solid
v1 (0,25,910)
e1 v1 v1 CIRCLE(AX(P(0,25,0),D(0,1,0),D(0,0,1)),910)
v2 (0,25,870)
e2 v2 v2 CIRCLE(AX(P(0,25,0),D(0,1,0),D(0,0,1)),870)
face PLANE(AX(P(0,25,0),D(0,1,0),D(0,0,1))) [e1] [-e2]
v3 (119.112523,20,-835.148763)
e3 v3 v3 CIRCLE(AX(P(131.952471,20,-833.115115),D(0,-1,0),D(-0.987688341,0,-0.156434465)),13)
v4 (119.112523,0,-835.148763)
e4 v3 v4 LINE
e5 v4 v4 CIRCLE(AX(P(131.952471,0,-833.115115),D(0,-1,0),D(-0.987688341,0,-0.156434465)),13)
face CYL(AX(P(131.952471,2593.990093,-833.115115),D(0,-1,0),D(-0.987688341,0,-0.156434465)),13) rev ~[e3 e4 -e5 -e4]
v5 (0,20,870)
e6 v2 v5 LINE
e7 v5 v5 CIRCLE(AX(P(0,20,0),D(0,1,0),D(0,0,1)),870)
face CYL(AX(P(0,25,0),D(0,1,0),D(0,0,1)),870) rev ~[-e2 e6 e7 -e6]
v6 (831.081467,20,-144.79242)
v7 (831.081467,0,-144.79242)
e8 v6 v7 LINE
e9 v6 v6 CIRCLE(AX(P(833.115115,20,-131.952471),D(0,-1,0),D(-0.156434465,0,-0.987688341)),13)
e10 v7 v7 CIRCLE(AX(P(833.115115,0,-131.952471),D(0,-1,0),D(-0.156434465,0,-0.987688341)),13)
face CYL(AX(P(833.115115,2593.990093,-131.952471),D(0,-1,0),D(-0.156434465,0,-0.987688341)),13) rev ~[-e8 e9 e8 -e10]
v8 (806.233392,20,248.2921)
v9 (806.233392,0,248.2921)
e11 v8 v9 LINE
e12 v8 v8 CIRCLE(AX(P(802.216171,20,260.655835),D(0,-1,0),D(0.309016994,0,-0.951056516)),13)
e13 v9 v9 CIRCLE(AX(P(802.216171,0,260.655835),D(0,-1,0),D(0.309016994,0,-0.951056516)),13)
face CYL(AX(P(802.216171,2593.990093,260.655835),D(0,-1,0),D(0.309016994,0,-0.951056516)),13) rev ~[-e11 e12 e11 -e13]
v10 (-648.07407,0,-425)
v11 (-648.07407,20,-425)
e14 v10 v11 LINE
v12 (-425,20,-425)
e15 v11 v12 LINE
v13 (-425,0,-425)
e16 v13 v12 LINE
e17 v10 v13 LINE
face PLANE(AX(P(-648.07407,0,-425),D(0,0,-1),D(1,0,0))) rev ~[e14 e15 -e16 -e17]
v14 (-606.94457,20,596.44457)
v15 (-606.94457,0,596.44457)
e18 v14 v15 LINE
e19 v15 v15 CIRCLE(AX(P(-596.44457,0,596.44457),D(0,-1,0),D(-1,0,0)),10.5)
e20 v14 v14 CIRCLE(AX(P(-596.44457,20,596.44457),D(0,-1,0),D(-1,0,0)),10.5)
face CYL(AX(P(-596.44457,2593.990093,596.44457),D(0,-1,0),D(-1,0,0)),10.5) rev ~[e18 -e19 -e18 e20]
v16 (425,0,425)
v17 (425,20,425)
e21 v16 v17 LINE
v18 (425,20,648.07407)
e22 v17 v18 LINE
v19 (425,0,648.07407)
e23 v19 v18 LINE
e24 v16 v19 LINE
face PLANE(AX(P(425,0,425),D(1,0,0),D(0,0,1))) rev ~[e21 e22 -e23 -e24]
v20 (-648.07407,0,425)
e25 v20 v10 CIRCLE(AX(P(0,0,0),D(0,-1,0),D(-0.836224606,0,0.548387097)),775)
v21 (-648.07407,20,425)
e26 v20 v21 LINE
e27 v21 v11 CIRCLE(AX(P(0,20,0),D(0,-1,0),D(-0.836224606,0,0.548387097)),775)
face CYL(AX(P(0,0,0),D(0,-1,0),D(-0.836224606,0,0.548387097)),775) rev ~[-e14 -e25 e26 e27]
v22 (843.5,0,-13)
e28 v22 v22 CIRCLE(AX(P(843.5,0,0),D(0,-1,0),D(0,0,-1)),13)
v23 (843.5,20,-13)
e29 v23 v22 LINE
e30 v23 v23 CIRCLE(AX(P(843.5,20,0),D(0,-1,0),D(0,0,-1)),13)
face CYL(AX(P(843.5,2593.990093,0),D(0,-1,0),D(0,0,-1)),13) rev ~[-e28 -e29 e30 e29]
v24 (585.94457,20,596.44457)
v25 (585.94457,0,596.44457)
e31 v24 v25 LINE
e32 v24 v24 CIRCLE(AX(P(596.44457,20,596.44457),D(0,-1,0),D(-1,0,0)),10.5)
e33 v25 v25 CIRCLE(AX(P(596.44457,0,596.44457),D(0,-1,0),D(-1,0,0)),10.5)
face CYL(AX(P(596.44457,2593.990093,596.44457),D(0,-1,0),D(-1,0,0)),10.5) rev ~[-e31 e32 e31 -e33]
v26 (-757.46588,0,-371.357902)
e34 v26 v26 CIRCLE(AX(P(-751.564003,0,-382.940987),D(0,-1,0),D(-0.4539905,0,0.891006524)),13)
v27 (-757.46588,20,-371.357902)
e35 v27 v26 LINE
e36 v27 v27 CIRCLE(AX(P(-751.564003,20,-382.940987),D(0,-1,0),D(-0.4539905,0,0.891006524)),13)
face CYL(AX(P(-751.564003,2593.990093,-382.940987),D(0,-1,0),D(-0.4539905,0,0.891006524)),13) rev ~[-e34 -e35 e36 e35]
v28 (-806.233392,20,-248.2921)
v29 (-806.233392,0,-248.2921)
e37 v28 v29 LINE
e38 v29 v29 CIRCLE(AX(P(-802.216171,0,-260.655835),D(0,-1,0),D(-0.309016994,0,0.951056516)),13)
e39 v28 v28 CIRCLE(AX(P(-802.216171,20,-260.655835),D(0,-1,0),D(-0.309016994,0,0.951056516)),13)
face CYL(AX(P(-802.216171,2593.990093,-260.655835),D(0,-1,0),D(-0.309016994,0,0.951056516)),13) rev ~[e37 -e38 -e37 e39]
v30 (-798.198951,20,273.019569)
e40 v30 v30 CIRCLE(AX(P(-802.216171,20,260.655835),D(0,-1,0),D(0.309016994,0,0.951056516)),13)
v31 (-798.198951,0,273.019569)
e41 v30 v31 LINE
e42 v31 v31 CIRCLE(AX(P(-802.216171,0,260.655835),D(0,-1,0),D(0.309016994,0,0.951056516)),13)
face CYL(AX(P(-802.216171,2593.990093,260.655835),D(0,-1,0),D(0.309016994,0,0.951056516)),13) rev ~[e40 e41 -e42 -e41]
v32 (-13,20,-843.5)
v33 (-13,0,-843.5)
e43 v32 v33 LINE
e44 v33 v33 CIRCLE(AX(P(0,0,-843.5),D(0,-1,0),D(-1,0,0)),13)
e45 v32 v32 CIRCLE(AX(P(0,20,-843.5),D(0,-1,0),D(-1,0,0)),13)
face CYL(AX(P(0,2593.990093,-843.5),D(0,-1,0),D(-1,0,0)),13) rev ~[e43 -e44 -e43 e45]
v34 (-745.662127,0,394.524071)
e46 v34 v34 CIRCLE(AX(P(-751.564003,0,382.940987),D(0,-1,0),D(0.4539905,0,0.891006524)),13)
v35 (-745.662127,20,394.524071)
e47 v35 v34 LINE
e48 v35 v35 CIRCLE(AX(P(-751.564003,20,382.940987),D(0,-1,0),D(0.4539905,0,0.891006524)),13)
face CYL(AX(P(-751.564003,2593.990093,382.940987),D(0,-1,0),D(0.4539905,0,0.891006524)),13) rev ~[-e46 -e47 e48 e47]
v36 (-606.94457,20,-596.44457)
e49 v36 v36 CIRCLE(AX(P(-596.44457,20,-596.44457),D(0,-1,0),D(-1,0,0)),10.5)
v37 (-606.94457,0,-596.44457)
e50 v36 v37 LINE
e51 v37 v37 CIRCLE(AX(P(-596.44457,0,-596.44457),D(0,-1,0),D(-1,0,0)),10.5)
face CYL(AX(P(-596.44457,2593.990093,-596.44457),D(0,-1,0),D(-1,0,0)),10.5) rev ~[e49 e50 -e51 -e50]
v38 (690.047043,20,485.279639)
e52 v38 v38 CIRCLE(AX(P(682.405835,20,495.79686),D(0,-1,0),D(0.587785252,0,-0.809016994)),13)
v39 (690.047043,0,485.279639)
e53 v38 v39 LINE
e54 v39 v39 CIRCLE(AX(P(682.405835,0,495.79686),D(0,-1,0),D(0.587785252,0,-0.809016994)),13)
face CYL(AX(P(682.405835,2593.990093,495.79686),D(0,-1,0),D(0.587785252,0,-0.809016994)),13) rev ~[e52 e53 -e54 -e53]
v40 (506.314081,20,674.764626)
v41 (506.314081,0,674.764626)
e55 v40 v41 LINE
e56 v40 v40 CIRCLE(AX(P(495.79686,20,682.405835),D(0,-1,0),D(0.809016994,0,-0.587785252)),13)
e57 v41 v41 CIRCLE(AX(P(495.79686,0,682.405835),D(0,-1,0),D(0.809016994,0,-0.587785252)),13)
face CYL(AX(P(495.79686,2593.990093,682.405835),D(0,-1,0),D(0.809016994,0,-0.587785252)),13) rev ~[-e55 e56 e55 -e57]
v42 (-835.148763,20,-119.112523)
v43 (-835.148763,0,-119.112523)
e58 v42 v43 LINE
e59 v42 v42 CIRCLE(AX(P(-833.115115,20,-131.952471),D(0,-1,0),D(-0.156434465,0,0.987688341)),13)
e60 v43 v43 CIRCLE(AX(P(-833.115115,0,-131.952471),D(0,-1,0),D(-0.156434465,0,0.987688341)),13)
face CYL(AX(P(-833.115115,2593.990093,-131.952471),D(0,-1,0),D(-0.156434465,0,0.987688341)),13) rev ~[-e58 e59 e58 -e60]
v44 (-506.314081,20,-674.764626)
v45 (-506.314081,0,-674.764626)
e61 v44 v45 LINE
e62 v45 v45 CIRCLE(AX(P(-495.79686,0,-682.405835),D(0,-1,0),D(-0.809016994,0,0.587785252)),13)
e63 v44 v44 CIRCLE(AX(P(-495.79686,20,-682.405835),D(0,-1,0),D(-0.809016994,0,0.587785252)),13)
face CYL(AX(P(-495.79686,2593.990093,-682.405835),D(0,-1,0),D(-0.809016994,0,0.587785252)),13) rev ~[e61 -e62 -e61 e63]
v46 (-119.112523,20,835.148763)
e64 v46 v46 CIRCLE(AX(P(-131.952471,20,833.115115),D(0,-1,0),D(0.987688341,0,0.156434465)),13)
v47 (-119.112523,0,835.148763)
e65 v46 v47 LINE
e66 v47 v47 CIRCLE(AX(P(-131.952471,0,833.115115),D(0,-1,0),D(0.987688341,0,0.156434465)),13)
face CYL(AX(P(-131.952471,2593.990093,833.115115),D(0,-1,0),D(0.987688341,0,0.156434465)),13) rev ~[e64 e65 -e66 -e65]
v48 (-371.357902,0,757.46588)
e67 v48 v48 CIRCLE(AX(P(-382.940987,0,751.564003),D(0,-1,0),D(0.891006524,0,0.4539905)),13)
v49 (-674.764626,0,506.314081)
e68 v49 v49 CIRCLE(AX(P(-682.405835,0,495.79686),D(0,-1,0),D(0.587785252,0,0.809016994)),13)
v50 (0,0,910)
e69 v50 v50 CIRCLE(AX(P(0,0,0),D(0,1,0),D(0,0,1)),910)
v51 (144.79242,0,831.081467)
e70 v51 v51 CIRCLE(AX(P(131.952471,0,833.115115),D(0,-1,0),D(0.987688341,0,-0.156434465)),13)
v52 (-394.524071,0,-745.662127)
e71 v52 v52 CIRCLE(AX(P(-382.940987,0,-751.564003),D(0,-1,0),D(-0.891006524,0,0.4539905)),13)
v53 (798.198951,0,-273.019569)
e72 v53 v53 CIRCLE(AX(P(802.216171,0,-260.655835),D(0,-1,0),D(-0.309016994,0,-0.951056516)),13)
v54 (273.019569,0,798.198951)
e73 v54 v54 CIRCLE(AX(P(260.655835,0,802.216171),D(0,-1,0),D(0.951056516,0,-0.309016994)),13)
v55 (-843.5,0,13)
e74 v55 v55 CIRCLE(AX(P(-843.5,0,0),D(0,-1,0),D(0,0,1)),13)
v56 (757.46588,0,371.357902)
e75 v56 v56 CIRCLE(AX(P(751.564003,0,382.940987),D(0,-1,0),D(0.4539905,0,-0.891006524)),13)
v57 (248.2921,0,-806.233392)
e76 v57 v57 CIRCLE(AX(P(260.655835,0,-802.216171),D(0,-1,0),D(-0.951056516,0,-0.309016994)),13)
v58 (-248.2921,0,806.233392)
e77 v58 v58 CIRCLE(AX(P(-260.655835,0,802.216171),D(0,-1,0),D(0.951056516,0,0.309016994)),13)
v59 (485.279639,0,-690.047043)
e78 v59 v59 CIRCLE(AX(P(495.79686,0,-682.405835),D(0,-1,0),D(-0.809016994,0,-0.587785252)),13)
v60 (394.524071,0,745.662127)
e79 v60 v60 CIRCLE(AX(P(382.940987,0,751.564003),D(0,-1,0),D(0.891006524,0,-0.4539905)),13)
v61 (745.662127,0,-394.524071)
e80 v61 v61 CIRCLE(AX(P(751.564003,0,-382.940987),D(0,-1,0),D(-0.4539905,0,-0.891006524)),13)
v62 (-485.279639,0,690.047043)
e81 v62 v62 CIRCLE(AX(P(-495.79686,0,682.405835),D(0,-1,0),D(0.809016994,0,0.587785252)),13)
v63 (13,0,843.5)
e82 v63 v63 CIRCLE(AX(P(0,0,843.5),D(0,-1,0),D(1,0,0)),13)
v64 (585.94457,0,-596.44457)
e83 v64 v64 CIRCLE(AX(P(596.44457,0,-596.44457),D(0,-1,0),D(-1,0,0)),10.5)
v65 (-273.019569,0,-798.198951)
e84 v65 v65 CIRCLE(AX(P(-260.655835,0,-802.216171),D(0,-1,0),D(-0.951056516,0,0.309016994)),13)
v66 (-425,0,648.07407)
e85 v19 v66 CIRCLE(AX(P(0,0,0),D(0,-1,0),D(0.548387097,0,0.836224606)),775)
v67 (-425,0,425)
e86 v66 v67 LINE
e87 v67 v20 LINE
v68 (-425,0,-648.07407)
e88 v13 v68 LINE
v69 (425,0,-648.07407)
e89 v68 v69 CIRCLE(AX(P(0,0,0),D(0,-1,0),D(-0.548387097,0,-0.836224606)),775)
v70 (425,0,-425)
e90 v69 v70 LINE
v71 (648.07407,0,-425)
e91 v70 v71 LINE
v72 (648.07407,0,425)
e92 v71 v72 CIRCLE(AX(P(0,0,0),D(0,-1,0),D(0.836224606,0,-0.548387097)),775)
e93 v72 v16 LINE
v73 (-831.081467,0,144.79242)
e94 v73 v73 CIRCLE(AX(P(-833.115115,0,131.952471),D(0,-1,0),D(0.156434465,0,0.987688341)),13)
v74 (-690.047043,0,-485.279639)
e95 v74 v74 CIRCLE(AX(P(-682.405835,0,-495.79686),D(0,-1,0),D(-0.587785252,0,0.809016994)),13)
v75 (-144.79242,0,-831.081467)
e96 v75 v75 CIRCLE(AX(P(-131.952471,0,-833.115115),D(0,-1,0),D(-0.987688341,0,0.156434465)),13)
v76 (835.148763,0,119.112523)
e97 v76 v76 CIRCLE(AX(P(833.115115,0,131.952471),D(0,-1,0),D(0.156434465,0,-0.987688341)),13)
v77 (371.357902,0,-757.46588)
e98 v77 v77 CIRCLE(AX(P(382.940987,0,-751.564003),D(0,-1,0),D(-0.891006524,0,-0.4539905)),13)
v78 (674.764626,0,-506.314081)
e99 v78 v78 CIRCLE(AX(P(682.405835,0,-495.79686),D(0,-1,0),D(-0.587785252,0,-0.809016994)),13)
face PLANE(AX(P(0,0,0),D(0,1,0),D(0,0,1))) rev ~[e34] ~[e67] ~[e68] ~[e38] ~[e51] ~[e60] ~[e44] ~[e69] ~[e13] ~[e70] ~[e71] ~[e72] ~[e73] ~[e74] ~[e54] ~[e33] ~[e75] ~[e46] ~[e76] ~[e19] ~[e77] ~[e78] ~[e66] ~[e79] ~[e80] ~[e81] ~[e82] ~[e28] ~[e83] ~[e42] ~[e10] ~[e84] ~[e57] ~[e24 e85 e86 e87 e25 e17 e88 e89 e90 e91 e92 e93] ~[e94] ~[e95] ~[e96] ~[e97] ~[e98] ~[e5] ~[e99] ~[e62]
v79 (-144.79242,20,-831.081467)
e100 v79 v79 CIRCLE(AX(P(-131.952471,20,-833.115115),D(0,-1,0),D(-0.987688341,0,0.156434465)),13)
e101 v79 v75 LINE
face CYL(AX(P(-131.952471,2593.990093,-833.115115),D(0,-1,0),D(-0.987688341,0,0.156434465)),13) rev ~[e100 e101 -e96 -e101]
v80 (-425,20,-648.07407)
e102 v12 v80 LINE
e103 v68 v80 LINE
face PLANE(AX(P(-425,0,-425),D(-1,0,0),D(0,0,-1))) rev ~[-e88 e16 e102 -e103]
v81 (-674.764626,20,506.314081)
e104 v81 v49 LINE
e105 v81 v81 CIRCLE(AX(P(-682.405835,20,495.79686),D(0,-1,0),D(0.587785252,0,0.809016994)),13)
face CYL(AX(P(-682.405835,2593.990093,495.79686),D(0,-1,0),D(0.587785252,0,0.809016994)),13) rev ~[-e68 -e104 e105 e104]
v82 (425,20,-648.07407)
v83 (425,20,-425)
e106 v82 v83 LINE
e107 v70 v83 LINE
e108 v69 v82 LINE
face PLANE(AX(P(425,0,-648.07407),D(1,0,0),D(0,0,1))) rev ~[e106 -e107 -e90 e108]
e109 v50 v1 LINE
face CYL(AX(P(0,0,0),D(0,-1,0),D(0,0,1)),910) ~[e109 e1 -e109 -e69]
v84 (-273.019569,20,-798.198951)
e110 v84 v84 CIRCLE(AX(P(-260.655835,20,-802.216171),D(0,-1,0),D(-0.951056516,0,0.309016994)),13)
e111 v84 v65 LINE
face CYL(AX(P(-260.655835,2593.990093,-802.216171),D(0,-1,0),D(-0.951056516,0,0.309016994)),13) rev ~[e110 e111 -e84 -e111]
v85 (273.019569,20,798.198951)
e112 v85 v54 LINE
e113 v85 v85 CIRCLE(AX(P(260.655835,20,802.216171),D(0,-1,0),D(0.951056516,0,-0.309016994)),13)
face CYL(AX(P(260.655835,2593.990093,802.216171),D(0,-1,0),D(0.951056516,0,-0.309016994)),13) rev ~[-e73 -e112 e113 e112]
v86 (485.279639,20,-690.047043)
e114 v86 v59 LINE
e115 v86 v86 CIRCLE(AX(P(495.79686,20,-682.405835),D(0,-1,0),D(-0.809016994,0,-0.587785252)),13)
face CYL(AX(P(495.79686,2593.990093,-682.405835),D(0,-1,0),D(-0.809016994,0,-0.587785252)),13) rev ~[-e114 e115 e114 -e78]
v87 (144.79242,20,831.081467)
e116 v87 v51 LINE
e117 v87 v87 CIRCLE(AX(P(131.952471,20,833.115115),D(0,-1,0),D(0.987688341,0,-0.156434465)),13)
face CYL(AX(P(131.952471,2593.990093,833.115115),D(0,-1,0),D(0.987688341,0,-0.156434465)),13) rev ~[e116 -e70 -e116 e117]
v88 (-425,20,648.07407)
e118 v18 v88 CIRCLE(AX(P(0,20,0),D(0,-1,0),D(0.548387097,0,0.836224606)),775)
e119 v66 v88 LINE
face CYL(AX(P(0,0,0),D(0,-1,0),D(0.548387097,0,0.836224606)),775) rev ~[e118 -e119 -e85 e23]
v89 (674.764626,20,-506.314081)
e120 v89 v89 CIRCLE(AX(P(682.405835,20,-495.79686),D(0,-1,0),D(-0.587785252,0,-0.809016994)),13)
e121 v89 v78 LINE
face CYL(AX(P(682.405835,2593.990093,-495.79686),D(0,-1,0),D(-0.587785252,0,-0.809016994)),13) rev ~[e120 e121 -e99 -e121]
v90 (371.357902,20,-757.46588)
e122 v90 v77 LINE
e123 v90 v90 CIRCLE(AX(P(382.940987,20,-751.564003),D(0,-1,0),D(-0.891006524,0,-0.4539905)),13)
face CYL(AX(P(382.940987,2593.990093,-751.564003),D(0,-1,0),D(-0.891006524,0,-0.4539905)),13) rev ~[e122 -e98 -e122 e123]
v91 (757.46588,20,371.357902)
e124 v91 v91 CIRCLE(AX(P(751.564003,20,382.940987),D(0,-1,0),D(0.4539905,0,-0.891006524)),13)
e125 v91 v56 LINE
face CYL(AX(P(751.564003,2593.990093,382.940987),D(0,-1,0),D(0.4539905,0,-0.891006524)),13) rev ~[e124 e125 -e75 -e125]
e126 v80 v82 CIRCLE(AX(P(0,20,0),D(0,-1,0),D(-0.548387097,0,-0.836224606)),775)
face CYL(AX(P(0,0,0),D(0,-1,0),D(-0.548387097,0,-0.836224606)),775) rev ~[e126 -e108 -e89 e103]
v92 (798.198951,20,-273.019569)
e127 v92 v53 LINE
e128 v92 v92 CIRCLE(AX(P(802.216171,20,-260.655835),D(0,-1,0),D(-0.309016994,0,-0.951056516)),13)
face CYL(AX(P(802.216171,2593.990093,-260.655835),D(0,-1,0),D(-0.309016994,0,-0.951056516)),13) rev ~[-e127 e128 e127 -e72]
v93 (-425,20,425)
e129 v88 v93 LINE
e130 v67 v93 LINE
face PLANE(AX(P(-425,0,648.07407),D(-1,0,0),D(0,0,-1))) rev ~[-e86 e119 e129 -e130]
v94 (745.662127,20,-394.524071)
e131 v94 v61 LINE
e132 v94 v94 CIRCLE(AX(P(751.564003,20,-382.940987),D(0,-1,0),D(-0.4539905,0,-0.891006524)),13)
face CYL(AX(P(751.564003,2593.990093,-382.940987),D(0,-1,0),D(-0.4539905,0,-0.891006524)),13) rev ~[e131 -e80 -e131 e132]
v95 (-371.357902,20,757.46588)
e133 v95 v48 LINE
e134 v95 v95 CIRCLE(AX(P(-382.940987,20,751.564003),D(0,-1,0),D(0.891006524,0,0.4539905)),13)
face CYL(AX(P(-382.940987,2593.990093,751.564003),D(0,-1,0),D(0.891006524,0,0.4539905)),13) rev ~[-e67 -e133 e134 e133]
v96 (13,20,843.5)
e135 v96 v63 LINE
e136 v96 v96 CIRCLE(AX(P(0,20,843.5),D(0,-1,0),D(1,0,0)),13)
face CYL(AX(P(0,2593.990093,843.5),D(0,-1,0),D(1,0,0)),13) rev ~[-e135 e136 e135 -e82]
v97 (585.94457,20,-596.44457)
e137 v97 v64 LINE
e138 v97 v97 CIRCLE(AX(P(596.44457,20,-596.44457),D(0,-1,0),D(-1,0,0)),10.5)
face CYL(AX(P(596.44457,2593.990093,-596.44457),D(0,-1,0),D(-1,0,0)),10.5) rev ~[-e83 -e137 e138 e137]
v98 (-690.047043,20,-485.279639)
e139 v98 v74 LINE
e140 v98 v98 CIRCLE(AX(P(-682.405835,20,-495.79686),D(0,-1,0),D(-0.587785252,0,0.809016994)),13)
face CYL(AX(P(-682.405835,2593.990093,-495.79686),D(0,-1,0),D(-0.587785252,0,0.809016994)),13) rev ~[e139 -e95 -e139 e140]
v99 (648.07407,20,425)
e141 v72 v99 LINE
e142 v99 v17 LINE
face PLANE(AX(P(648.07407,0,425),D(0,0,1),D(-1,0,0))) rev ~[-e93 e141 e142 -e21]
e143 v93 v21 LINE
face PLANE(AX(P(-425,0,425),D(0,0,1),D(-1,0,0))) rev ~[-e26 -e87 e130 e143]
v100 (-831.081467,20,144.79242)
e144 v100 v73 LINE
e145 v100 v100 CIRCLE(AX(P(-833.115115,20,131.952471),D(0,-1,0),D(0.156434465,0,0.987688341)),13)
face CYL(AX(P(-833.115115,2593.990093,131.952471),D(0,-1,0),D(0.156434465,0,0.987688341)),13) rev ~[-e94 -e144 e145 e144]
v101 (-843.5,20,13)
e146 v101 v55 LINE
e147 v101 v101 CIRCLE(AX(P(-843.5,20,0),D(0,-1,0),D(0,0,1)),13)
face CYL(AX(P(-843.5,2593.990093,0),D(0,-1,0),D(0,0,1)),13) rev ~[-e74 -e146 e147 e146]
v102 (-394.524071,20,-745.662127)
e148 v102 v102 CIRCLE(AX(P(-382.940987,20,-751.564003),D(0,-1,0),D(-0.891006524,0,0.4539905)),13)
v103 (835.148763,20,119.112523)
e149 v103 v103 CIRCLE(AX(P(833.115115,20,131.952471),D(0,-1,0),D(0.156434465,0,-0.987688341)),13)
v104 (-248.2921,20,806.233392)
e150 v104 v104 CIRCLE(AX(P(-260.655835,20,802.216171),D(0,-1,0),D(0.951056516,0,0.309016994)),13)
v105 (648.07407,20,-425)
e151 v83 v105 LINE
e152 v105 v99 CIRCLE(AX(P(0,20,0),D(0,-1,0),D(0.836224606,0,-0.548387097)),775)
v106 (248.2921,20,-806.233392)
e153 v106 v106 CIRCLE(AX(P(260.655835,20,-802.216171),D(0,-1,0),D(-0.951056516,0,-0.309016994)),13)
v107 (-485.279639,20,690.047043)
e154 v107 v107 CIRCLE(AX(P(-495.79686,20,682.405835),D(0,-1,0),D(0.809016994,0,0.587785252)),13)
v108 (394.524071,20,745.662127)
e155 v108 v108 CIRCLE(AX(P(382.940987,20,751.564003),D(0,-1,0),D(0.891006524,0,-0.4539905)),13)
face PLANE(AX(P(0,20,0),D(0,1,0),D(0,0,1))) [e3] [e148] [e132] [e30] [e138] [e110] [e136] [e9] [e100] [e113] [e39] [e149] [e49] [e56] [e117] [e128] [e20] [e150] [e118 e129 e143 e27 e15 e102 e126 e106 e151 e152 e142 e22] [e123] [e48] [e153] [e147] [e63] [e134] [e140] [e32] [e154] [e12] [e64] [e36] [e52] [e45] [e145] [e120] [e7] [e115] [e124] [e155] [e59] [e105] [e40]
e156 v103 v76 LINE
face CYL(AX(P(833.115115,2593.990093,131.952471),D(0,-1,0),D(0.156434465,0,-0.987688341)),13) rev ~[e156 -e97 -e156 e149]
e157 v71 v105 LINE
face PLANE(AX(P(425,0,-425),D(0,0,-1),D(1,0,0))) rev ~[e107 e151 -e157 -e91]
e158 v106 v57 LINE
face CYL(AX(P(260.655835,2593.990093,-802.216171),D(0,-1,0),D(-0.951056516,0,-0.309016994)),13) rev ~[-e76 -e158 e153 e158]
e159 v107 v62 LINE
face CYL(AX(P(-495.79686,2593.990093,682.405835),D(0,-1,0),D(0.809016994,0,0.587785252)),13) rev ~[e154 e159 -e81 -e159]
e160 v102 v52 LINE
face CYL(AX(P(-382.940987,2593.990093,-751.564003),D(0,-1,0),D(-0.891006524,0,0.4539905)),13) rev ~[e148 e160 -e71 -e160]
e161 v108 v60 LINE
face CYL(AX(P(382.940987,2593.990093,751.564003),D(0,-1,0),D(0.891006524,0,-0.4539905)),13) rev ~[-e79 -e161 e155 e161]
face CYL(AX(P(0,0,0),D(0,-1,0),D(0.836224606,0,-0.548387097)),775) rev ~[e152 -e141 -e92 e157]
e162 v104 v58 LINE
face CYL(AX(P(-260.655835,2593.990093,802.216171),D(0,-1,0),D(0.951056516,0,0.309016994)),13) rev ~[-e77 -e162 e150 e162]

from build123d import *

# Parameters (mm, degrees)
SKETCH_1_R               = 910
EXTRUDE_1_DEPTH          = 25
SKETCH_2_R               = 870
CUT_EXTRUDE_1_DEPTH      = 5
HOLE_WIZARD_26_1_D       = 26
PATTERN_CIRCULAR_1_COUNT = 40
HOLE_WIZARD_M24_1_D      = 21


with BuildPart() as part:
    # 草图1 → 凸台-拉伸1 (new body)
    with BuildSketch(Plane(origin=(0, 0, 0), x_dir=(1, 0, 0), z_dir=(0, 1, 0))):
        with Locations(Location((0, 0, 0), (0, 0, 270))):
            Circle(SKETCH_1_R)
        with BuildLine():
            Line((-648.074069841, 425), (-425, 425))
            Line((-425, 425), (-425, 648.074069841))
            ThreePointArc((-425, 648.074069841), (0, 775), (425, 648.074069841))
            Line((425, 648.074069841), (425, 425))
            Line((425, 425), (648.074069841, 425))
            ThreePointArc((648.074069841, 425), (775, 0), (648.074069841, -425))
            Line((648.074069841, -425), (425, -425))
            Line((425, -425), (425, -648.074069841))
            ThreePointArc((425, -648.074069841), (0, -775), (-425, -648.074069841))
            Line((-425, -648.074069841), (-425, -425))
            Line((-425, -425), (-648.074069841, -425))
            ThreePointArc((-648.074069841, -425), (-775, 0), (-648.074069841, 425))
        make_face(mode=Mode.SUBTRACT)
    extrude(amount=EXTRUDE_1_DEPTH)

    # 草图2 → 切除-拉伸1 (cut)
    with BuildSketch(Plane(origin=(0, 25, 0), x_dir=(1, 0, 0), z_dir=(0, 1, 0))):
        with Locations(Location((0, 0, 0), (0, 0, 270))):
            Circle(SKETCH_2_R)
    extrude(amount=-CUT_EXTRUDE_1_DEPTH, mode=Mode.SUBTRACT)

    # Ø26 直径孔1 (through all)
    with Locations(Plane(origin=(0, 20, 0), x_dir=(1, 0, 0), z_dir=(0, 1, 0))):
        with Locations((0, 843.5)):
            hole_wizard_26_1 = Hole(HOLE_WIZARD_26_1_D / 2)

    # 阵列(圆周)1: Ø26 直径孔1 ×40 about axis, 4 skipped
    pattern_circular_1_axis = Axis((0, 0, 0), (0, 1, 0))
    add([hole_wizard_26_1.rotate(pattern_circular_1_axis, i * 360 / PATTERN_CIRCULAR_1_COUNT) for i in range(1, PATTERN_CIRCULAR_1_COUNT) if i not in (5, 15, 25, 35)], mode=Mode.SUBTRACT)

    # M24 螺纹孔1 (through all)
    with Locations(Plane(origin=(0, 20, 0), x_dir=(1, 0, 0), z_dir=(0, 1, 0))):
        with Locations((-596.444569931, 596.444569931), (596.444569931, 596.444569931), (596.444569931, -596.444569931), (-596.444569931, -596.444569931)):
            Hole(HOLE_WIZARD_M24_1_D / 2)


solid = part.part
